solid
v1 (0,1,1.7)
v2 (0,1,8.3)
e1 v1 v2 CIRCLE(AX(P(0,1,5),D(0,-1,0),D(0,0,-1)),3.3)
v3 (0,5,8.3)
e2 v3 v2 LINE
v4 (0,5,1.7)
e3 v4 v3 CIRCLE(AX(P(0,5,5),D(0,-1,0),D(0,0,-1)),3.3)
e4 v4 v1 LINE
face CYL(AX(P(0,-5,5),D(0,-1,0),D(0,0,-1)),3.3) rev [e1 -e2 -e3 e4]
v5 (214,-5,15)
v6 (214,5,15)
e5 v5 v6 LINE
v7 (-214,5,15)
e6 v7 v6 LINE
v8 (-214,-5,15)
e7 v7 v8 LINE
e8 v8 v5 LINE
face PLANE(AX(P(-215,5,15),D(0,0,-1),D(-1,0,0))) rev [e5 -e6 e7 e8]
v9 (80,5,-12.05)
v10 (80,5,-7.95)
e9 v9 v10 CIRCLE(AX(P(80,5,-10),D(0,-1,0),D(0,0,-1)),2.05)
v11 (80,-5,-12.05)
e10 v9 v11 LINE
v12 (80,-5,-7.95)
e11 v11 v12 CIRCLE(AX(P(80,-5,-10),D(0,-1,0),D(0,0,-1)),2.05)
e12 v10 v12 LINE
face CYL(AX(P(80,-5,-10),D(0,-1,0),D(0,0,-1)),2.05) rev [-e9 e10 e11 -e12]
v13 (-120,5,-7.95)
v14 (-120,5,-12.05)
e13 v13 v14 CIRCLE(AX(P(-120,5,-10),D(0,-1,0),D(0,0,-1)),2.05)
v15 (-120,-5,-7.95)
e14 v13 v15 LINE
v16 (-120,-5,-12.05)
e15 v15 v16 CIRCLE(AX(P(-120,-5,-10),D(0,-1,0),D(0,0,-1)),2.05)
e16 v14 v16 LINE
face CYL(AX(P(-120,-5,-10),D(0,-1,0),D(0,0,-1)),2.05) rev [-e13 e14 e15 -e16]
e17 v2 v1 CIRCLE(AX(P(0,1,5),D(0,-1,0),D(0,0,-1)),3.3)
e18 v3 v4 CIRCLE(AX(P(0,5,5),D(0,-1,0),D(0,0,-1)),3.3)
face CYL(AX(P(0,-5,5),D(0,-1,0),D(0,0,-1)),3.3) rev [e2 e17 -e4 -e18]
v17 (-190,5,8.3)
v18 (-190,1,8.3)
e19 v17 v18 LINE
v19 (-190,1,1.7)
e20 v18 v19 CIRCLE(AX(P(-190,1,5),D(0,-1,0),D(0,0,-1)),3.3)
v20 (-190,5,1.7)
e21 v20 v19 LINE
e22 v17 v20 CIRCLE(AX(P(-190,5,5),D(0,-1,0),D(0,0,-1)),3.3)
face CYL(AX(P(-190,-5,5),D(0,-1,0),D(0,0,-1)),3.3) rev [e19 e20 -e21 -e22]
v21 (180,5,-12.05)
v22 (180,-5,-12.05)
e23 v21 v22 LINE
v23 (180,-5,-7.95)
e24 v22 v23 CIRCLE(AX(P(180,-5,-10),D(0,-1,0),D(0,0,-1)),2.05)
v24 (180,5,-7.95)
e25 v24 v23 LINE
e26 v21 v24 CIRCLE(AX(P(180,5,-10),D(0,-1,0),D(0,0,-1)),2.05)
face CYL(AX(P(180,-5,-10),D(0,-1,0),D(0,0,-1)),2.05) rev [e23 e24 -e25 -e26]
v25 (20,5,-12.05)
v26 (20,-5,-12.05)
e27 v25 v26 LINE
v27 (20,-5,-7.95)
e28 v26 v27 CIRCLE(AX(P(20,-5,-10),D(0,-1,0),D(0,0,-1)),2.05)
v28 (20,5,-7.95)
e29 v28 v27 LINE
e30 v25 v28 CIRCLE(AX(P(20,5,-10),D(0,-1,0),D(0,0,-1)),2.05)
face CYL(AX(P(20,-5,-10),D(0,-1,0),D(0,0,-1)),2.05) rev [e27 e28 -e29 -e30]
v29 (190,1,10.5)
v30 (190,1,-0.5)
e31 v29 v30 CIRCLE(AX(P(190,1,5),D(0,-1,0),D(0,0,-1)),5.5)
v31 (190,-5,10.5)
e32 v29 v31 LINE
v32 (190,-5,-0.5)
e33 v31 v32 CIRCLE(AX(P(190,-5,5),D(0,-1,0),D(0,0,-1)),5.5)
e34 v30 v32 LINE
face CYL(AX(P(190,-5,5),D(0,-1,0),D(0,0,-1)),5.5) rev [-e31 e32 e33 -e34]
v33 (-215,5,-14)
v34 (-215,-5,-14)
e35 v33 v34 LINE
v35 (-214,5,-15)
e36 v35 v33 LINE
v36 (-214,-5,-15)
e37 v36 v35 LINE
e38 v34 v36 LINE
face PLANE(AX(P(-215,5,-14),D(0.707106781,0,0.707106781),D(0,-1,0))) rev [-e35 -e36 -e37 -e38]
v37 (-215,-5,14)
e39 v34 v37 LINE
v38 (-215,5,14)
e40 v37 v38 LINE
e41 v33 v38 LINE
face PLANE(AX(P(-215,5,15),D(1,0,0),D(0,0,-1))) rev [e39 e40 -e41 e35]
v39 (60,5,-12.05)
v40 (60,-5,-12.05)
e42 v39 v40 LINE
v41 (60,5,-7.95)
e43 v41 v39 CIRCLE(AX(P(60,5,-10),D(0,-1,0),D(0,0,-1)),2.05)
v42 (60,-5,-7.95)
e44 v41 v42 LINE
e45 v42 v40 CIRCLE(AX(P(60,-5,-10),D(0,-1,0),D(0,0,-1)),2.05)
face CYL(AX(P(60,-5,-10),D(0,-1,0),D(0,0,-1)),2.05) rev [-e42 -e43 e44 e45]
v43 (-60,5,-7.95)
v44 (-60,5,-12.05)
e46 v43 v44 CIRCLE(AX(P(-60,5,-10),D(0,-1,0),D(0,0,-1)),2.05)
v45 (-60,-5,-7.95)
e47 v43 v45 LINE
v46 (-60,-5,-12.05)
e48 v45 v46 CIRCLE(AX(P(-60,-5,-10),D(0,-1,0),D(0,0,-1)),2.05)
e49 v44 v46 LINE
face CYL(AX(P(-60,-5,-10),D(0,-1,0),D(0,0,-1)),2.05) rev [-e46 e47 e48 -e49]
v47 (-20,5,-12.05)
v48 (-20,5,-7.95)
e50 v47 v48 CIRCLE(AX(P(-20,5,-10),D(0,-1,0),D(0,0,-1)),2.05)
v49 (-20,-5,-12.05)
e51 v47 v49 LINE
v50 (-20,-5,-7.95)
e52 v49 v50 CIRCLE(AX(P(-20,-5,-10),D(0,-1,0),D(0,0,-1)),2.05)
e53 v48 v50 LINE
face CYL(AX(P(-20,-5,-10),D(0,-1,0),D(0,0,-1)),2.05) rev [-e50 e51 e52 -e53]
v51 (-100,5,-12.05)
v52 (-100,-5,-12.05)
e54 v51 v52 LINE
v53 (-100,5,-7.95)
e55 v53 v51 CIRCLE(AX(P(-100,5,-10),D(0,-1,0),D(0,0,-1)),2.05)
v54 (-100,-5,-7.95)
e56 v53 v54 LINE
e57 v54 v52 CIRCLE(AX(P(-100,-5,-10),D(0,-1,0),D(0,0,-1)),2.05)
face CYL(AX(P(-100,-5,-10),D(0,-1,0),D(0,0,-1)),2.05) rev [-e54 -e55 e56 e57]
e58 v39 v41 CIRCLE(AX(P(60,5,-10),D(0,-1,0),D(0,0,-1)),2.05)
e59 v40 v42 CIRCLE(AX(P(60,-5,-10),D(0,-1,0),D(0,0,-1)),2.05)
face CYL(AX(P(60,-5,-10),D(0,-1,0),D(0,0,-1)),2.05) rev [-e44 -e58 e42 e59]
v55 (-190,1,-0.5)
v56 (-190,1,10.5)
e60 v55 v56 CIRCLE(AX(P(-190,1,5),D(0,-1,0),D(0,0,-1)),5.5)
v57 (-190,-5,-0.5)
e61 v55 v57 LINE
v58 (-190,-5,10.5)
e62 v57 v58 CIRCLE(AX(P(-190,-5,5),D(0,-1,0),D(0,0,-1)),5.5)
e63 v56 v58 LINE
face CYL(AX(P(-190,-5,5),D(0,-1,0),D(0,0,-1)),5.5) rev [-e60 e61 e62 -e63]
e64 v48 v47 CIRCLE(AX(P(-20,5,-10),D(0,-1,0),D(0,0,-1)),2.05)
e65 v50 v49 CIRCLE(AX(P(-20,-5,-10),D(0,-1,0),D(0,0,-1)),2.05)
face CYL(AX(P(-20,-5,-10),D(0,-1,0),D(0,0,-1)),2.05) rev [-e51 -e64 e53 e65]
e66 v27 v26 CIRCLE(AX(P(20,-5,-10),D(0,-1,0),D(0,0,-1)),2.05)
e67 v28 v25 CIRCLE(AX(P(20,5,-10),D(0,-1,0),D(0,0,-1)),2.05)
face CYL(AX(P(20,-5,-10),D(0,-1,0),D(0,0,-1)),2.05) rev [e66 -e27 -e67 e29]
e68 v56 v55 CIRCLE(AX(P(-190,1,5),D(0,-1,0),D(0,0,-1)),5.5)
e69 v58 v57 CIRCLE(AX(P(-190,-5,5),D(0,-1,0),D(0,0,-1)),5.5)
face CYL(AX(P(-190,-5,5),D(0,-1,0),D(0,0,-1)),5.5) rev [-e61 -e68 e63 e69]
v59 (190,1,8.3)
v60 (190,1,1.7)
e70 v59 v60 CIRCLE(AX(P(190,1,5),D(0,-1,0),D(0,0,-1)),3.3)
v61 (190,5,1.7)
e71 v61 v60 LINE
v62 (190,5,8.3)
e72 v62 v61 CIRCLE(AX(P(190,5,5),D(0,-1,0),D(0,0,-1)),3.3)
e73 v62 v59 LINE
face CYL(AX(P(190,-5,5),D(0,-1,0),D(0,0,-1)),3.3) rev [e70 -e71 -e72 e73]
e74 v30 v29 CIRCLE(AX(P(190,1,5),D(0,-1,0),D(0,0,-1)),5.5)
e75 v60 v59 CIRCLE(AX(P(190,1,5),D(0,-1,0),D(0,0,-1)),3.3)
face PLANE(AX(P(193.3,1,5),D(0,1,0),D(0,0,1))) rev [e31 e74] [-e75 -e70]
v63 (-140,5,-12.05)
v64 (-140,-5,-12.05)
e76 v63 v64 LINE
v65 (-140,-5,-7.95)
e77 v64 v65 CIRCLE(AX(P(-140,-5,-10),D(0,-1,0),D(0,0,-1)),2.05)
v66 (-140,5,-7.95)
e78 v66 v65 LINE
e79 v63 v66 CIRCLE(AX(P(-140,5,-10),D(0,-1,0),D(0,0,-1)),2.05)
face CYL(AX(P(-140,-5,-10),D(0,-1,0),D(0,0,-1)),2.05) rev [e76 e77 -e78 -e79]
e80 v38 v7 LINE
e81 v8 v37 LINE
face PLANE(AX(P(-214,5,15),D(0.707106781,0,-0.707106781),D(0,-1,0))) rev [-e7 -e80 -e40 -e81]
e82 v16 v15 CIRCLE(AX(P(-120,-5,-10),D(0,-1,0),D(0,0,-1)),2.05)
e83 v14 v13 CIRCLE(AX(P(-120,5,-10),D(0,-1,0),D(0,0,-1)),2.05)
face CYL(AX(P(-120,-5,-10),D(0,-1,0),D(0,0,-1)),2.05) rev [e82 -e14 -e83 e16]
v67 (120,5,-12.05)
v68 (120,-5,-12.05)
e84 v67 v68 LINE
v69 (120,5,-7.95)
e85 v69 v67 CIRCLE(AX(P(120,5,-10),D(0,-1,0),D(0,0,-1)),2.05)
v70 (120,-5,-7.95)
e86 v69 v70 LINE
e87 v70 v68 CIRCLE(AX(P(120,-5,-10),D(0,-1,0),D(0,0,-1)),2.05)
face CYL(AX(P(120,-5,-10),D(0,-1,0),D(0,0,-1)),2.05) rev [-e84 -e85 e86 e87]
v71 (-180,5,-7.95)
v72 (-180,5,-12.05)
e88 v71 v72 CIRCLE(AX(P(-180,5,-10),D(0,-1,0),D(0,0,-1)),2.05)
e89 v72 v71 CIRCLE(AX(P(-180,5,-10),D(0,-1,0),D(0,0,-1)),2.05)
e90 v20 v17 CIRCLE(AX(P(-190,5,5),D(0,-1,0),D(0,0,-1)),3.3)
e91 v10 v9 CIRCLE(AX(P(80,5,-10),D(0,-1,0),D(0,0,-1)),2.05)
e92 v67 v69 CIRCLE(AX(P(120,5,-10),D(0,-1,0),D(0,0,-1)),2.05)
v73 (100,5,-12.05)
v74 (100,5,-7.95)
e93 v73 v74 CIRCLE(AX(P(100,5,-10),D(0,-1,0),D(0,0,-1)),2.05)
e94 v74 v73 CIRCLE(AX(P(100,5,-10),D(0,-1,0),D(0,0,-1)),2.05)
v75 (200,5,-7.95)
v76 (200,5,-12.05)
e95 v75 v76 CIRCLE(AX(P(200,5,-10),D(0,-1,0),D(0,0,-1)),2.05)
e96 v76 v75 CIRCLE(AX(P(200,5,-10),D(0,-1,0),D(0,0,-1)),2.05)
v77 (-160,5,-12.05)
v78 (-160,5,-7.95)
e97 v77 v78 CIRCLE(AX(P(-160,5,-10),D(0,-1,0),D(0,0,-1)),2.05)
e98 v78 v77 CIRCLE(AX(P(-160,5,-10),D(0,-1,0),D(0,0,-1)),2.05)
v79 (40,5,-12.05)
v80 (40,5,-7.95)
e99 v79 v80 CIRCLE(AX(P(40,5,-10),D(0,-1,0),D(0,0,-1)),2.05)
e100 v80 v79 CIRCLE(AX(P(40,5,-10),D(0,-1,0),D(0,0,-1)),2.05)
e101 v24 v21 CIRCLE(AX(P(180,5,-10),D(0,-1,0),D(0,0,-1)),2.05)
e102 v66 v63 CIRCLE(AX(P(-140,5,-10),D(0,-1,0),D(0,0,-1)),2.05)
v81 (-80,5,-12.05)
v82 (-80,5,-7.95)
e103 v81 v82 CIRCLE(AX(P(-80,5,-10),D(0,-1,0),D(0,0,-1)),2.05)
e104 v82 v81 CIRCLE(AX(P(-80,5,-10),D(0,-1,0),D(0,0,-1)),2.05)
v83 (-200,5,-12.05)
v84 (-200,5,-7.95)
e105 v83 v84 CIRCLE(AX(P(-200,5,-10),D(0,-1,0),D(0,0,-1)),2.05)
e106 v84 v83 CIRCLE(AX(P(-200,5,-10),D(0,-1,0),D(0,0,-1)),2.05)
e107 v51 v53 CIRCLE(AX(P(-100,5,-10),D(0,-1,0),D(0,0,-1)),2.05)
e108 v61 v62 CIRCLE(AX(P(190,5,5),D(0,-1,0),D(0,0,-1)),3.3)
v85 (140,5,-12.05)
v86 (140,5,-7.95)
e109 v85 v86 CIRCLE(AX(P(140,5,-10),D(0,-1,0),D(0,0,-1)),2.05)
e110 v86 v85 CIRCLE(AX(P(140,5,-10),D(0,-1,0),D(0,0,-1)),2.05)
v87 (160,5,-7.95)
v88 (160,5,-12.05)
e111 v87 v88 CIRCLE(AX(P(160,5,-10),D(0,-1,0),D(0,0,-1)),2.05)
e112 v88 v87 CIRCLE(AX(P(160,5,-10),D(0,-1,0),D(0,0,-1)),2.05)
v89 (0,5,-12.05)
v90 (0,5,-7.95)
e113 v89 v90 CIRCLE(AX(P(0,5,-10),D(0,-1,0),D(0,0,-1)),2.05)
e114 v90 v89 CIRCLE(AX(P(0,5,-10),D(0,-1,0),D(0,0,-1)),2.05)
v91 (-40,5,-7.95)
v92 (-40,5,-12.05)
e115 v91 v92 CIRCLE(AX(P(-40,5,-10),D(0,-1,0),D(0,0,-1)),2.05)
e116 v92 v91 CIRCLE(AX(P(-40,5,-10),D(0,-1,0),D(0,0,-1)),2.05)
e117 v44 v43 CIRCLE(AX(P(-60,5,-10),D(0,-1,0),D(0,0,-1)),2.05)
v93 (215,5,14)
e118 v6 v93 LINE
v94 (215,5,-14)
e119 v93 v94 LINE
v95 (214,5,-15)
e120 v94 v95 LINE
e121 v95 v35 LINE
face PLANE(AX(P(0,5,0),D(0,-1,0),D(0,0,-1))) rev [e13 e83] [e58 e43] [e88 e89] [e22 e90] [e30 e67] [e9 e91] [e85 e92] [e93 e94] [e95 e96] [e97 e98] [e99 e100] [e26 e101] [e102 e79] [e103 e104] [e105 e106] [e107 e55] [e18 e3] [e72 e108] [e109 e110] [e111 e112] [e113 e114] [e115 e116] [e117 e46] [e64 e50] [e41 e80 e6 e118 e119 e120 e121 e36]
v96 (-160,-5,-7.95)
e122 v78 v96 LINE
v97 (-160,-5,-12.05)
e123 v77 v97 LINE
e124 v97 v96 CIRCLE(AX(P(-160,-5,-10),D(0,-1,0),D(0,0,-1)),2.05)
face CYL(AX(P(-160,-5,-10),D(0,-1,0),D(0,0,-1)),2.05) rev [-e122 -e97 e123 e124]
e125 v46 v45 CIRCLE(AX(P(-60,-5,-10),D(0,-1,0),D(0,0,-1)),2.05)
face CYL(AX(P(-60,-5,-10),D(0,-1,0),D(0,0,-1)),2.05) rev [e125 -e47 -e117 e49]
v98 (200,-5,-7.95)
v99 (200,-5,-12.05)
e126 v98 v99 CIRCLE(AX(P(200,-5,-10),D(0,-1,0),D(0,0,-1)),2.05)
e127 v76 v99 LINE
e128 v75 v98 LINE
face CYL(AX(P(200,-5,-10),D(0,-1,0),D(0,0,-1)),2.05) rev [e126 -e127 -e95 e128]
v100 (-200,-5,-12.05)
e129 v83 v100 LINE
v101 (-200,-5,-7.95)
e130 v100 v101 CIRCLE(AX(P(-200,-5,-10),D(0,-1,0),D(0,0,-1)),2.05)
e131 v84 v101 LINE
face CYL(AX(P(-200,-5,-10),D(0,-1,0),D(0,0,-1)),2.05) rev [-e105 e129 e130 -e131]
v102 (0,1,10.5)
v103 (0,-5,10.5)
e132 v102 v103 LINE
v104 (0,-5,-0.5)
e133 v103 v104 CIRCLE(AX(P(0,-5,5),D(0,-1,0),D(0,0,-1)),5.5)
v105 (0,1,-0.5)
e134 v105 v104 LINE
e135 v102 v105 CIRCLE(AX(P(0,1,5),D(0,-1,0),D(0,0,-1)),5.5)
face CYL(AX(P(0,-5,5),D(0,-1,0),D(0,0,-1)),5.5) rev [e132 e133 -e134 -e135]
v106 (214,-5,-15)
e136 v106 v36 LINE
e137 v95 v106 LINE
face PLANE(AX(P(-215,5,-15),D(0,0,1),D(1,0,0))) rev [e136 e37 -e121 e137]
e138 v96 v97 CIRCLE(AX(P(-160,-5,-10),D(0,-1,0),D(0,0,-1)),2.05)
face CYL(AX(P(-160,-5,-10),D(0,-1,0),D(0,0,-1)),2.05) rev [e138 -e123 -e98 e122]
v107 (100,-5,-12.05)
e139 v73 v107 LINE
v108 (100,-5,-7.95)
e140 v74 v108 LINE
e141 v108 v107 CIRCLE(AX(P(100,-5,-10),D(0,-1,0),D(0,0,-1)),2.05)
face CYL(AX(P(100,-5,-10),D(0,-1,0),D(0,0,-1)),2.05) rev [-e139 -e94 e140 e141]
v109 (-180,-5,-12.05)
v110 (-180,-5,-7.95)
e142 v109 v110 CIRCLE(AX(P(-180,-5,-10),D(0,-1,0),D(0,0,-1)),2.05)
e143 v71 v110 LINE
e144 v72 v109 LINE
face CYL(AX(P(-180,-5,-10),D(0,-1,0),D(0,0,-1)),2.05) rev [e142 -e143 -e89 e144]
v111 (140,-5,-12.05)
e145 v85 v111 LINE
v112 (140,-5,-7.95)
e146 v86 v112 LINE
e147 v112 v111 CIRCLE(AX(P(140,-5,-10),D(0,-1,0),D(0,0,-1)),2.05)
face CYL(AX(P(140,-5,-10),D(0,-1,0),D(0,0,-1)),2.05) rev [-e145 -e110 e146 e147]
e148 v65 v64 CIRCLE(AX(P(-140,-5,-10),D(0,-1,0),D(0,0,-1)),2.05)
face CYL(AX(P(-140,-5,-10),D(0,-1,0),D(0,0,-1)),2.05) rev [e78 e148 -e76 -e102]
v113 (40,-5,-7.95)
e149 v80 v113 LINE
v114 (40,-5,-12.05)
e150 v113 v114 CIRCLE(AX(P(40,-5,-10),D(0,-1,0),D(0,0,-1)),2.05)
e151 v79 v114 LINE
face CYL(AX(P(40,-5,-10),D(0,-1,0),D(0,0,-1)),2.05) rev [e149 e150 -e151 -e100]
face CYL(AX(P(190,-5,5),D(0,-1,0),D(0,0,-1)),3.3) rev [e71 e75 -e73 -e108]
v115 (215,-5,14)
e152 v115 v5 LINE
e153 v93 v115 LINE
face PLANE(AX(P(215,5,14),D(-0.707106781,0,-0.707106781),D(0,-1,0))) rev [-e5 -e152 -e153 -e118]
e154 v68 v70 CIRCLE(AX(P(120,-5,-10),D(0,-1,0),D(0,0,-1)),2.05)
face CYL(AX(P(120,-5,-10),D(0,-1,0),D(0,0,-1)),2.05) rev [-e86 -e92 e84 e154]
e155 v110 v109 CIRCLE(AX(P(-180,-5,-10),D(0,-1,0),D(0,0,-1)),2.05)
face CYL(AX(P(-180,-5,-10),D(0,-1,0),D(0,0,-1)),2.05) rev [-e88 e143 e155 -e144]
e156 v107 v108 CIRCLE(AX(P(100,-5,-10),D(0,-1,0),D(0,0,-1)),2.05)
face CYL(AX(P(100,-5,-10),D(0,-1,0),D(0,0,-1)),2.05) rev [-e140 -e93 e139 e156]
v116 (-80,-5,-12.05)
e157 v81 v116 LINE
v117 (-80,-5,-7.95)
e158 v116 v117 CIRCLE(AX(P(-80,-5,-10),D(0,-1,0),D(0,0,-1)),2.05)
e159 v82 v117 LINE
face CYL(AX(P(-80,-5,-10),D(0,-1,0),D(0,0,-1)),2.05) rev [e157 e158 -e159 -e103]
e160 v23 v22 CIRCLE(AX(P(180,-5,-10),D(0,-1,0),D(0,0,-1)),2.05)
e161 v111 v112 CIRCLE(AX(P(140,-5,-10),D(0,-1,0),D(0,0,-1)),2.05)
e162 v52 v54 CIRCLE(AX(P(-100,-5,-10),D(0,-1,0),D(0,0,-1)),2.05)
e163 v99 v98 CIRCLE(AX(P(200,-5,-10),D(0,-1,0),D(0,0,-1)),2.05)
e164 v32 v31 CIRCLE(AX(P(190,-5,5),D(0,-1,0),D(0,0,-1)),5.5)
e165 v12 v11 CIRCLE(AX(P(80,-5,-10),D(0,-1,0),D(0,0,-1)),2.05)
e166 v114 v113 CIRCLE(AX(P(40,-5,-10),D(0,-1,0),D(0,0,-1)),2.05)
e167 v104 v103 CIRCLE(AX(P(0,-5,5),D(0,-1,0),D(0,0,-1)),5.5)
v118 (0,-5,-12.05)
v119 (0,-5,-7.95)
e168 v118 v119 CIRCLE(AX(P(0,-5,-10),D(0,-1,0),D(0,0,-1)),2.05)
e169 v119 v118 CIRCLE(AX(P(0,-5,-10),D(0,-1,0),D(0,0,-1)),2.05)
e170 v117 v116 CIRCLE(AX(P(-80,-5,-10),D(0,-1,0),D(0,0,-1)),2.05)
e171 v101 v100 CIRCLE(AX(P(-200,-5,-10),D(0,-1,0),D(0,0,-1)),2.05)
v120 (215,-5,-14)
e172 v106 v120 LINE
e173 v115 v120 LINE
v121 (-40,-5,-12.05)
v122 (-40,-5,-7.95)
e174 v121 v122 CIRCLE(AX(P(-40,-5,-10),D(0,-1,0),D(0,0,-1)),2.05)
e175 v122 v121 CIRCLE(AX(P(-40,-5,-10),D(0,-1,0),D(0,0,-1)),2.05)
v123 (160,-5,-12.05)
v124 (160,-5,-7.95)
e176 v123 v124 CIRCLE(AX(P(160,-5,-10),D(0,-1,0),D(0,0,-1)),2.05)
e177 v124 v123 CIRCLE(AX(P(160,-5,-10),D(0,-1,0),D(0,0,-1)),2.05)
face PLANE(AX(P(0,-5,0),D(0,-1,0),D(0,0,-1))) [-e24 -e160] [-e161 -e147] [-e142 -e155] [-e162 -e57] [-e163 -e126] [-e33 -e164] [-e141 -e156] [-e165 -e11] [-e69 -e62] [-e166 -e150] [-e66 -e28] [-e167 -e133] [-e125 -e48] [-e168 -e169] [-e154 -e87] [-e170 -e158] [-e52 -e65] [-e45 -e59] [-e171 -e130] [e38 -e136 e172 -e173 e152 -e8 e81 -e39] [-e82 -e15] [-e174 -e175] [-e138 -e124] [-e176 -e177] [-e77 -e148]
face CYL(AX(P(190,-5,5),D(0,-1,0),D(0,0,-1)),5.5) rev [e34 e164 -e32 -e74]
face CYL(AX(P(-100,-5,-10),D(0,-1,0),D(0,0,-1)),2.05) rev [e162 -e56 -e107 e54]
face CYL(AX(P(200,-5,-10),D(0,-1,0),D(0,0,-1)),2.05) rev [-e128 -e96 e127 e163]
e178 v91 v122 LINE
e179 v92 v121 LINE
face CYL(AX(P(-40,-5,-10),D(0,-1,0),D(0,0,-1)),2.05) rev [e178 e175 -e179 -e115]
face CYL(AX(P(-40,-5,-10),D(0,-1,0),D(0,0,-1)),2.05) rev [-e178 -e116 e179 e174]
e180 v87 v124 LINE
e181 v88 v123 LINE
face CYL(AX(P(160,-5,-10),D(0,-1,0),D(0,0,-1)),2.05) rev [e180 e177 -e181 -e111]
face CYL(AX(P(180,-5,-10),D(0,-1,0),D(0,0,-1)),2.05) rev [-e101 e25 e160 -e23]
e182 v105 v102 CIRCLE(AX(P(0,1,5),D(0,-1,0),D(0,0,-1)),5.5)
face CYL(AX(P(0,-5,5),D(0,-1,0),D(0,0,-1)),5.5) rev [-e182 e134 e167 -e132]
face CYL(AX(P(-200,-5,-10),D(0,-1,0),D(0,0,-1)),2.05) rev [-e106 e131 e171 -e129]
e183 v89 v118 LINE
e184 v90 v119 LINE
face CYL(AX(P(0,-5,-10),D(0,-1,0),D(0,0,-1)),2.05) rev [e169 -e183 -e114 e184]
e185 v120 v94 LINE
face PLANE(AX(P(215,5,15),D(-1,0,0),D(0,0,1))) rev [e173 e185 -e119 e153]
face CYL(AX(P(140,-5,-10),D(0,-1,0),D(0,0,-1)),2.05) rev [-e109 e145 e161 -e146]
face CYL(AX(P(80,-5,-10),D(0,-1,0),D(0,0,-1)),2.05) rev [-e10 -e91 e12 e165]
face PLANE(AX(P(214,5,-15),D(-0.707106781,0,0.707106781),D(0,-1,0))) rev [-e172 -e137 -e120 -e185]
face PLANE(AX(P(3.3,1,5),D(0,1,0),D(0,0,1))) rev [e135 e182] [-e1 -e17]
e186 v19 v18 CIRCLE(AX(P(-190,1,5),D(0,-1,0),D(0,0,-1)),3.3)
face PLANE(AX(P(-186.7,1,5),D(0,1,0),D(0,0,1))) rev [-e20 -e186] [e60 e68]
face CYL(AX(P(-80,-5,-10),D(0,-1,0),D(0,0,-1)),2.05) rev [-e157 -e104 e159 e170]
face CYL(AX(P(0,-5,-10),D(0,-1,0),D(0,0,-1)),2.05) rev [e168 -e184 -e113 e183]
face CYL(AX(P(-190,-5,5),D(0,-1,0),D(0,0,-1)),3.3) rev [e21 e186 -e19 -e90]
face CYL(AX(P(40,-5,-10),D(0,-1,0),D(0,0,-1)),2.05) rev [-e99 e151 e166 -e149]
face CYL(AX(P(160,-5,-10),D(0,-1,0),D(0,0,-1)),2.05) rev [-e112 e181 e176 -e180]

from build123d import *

# Parameters (mm, degrees)
SKETCH_1_W                  = 430
SKETCH_1_H                  = 30
EXTRUDE_1_DEPTH             = 5
CHAMFER_1_SIZE              = 1
HOLE_WIZARD_1_D             = 6.6
HOLE_WIZARD_1_CBORE_D       = 11
HOLE_WIZARD_1_CBORE_DEPTH   = 6
HOLE_WIZARD_4_1_4_1_1_D     = 4.1
HOLE_WIZARD_4_1_4_1_1_DEPTH = 10
HOLE_WIZARD_4_1_4_1_1_TIP   = 1.231764269


with BuildPart() as part:
    # 草图1 → 凸台-拉伸1 (new, symmetric)
    with BuildSketch(Plane(origin=(0, 0, 0), x_dir=(1, 0, 0), z_dir=(0, 1, 0))):
        Rectangle(SKETCH_1_W, SKETCH_1_H)
    extrude(amount=EXTRUDE_1_DEPTH, both=True)

    # 倒角1
    chamfer_1_edges = [part.edges().sort_by_distance(p)[0] for p in [
        (215, 0, 15),
        (-215, 0, 15),
        (-215, 0, -15),
        (215, 0, -15),
    ]]
    chamfer(chamfer_1_edges, length=CHAMFER_1_SIZE)

    # 打孔尺寸(%根据)内六角圆柱头螺钉的类型1 (through all)
    with Locations(Plane(origin=(0, -5, 0), x_dir=(-1, 0, 0), z_dir=(0, -1, 0))):
        with Locations((-190, -5), (0, -5), (190, -5)):
            CounterBoreHole(HOLE_WIZARD_1_D / 2, HOLE_WIZARD_1_CBORE_D / 2, HOLE_WIZARD_1_CBORE_DEPTH)

    # Ø4.1 (4.1) 直径孔1
    with Locations(Plane(origin=(0, -5, -18.75), x_dir=(-1, 0, 0), z_dir=(0, -1, 0))):
        with Locations((-200, -8.75), (-180, -8.75), (-160, -8.75), (-140, -8.75), (-120, -8.75), (-100, -8.75), (-80, -8.75), (-60, -8.75), (-40, -8.75), (-20, -8.75), (0, -8.75), (20, -8.75), (40, -8.75), (60, -8.75), (80, -8.75), (100, -8.75), (120, -8.75), (140, -8.75), (160, -8.75), (180, -8.75), (200, -8.75)):
            Hole(HOLE_WIZARD_4_1_4_1_1_D / 2, depth=HOLE_WIZARD_4_1_4_1_1_DEPTH)
            with Locations((0, 0, -(HOLE_WIZARD_4_1_4_1_1_DEPTH + HOLE_WIZARD_4_1_4_1_1_TIP / 2))):  # 118° drill point
                Cone(0, HOLE_WIZARD_4_1_4_1_1_D / 2, HOLE_WIZARD_4_1_4_1_1_TIP, mode=Mode.SUBTRACT)


solid = part.part
